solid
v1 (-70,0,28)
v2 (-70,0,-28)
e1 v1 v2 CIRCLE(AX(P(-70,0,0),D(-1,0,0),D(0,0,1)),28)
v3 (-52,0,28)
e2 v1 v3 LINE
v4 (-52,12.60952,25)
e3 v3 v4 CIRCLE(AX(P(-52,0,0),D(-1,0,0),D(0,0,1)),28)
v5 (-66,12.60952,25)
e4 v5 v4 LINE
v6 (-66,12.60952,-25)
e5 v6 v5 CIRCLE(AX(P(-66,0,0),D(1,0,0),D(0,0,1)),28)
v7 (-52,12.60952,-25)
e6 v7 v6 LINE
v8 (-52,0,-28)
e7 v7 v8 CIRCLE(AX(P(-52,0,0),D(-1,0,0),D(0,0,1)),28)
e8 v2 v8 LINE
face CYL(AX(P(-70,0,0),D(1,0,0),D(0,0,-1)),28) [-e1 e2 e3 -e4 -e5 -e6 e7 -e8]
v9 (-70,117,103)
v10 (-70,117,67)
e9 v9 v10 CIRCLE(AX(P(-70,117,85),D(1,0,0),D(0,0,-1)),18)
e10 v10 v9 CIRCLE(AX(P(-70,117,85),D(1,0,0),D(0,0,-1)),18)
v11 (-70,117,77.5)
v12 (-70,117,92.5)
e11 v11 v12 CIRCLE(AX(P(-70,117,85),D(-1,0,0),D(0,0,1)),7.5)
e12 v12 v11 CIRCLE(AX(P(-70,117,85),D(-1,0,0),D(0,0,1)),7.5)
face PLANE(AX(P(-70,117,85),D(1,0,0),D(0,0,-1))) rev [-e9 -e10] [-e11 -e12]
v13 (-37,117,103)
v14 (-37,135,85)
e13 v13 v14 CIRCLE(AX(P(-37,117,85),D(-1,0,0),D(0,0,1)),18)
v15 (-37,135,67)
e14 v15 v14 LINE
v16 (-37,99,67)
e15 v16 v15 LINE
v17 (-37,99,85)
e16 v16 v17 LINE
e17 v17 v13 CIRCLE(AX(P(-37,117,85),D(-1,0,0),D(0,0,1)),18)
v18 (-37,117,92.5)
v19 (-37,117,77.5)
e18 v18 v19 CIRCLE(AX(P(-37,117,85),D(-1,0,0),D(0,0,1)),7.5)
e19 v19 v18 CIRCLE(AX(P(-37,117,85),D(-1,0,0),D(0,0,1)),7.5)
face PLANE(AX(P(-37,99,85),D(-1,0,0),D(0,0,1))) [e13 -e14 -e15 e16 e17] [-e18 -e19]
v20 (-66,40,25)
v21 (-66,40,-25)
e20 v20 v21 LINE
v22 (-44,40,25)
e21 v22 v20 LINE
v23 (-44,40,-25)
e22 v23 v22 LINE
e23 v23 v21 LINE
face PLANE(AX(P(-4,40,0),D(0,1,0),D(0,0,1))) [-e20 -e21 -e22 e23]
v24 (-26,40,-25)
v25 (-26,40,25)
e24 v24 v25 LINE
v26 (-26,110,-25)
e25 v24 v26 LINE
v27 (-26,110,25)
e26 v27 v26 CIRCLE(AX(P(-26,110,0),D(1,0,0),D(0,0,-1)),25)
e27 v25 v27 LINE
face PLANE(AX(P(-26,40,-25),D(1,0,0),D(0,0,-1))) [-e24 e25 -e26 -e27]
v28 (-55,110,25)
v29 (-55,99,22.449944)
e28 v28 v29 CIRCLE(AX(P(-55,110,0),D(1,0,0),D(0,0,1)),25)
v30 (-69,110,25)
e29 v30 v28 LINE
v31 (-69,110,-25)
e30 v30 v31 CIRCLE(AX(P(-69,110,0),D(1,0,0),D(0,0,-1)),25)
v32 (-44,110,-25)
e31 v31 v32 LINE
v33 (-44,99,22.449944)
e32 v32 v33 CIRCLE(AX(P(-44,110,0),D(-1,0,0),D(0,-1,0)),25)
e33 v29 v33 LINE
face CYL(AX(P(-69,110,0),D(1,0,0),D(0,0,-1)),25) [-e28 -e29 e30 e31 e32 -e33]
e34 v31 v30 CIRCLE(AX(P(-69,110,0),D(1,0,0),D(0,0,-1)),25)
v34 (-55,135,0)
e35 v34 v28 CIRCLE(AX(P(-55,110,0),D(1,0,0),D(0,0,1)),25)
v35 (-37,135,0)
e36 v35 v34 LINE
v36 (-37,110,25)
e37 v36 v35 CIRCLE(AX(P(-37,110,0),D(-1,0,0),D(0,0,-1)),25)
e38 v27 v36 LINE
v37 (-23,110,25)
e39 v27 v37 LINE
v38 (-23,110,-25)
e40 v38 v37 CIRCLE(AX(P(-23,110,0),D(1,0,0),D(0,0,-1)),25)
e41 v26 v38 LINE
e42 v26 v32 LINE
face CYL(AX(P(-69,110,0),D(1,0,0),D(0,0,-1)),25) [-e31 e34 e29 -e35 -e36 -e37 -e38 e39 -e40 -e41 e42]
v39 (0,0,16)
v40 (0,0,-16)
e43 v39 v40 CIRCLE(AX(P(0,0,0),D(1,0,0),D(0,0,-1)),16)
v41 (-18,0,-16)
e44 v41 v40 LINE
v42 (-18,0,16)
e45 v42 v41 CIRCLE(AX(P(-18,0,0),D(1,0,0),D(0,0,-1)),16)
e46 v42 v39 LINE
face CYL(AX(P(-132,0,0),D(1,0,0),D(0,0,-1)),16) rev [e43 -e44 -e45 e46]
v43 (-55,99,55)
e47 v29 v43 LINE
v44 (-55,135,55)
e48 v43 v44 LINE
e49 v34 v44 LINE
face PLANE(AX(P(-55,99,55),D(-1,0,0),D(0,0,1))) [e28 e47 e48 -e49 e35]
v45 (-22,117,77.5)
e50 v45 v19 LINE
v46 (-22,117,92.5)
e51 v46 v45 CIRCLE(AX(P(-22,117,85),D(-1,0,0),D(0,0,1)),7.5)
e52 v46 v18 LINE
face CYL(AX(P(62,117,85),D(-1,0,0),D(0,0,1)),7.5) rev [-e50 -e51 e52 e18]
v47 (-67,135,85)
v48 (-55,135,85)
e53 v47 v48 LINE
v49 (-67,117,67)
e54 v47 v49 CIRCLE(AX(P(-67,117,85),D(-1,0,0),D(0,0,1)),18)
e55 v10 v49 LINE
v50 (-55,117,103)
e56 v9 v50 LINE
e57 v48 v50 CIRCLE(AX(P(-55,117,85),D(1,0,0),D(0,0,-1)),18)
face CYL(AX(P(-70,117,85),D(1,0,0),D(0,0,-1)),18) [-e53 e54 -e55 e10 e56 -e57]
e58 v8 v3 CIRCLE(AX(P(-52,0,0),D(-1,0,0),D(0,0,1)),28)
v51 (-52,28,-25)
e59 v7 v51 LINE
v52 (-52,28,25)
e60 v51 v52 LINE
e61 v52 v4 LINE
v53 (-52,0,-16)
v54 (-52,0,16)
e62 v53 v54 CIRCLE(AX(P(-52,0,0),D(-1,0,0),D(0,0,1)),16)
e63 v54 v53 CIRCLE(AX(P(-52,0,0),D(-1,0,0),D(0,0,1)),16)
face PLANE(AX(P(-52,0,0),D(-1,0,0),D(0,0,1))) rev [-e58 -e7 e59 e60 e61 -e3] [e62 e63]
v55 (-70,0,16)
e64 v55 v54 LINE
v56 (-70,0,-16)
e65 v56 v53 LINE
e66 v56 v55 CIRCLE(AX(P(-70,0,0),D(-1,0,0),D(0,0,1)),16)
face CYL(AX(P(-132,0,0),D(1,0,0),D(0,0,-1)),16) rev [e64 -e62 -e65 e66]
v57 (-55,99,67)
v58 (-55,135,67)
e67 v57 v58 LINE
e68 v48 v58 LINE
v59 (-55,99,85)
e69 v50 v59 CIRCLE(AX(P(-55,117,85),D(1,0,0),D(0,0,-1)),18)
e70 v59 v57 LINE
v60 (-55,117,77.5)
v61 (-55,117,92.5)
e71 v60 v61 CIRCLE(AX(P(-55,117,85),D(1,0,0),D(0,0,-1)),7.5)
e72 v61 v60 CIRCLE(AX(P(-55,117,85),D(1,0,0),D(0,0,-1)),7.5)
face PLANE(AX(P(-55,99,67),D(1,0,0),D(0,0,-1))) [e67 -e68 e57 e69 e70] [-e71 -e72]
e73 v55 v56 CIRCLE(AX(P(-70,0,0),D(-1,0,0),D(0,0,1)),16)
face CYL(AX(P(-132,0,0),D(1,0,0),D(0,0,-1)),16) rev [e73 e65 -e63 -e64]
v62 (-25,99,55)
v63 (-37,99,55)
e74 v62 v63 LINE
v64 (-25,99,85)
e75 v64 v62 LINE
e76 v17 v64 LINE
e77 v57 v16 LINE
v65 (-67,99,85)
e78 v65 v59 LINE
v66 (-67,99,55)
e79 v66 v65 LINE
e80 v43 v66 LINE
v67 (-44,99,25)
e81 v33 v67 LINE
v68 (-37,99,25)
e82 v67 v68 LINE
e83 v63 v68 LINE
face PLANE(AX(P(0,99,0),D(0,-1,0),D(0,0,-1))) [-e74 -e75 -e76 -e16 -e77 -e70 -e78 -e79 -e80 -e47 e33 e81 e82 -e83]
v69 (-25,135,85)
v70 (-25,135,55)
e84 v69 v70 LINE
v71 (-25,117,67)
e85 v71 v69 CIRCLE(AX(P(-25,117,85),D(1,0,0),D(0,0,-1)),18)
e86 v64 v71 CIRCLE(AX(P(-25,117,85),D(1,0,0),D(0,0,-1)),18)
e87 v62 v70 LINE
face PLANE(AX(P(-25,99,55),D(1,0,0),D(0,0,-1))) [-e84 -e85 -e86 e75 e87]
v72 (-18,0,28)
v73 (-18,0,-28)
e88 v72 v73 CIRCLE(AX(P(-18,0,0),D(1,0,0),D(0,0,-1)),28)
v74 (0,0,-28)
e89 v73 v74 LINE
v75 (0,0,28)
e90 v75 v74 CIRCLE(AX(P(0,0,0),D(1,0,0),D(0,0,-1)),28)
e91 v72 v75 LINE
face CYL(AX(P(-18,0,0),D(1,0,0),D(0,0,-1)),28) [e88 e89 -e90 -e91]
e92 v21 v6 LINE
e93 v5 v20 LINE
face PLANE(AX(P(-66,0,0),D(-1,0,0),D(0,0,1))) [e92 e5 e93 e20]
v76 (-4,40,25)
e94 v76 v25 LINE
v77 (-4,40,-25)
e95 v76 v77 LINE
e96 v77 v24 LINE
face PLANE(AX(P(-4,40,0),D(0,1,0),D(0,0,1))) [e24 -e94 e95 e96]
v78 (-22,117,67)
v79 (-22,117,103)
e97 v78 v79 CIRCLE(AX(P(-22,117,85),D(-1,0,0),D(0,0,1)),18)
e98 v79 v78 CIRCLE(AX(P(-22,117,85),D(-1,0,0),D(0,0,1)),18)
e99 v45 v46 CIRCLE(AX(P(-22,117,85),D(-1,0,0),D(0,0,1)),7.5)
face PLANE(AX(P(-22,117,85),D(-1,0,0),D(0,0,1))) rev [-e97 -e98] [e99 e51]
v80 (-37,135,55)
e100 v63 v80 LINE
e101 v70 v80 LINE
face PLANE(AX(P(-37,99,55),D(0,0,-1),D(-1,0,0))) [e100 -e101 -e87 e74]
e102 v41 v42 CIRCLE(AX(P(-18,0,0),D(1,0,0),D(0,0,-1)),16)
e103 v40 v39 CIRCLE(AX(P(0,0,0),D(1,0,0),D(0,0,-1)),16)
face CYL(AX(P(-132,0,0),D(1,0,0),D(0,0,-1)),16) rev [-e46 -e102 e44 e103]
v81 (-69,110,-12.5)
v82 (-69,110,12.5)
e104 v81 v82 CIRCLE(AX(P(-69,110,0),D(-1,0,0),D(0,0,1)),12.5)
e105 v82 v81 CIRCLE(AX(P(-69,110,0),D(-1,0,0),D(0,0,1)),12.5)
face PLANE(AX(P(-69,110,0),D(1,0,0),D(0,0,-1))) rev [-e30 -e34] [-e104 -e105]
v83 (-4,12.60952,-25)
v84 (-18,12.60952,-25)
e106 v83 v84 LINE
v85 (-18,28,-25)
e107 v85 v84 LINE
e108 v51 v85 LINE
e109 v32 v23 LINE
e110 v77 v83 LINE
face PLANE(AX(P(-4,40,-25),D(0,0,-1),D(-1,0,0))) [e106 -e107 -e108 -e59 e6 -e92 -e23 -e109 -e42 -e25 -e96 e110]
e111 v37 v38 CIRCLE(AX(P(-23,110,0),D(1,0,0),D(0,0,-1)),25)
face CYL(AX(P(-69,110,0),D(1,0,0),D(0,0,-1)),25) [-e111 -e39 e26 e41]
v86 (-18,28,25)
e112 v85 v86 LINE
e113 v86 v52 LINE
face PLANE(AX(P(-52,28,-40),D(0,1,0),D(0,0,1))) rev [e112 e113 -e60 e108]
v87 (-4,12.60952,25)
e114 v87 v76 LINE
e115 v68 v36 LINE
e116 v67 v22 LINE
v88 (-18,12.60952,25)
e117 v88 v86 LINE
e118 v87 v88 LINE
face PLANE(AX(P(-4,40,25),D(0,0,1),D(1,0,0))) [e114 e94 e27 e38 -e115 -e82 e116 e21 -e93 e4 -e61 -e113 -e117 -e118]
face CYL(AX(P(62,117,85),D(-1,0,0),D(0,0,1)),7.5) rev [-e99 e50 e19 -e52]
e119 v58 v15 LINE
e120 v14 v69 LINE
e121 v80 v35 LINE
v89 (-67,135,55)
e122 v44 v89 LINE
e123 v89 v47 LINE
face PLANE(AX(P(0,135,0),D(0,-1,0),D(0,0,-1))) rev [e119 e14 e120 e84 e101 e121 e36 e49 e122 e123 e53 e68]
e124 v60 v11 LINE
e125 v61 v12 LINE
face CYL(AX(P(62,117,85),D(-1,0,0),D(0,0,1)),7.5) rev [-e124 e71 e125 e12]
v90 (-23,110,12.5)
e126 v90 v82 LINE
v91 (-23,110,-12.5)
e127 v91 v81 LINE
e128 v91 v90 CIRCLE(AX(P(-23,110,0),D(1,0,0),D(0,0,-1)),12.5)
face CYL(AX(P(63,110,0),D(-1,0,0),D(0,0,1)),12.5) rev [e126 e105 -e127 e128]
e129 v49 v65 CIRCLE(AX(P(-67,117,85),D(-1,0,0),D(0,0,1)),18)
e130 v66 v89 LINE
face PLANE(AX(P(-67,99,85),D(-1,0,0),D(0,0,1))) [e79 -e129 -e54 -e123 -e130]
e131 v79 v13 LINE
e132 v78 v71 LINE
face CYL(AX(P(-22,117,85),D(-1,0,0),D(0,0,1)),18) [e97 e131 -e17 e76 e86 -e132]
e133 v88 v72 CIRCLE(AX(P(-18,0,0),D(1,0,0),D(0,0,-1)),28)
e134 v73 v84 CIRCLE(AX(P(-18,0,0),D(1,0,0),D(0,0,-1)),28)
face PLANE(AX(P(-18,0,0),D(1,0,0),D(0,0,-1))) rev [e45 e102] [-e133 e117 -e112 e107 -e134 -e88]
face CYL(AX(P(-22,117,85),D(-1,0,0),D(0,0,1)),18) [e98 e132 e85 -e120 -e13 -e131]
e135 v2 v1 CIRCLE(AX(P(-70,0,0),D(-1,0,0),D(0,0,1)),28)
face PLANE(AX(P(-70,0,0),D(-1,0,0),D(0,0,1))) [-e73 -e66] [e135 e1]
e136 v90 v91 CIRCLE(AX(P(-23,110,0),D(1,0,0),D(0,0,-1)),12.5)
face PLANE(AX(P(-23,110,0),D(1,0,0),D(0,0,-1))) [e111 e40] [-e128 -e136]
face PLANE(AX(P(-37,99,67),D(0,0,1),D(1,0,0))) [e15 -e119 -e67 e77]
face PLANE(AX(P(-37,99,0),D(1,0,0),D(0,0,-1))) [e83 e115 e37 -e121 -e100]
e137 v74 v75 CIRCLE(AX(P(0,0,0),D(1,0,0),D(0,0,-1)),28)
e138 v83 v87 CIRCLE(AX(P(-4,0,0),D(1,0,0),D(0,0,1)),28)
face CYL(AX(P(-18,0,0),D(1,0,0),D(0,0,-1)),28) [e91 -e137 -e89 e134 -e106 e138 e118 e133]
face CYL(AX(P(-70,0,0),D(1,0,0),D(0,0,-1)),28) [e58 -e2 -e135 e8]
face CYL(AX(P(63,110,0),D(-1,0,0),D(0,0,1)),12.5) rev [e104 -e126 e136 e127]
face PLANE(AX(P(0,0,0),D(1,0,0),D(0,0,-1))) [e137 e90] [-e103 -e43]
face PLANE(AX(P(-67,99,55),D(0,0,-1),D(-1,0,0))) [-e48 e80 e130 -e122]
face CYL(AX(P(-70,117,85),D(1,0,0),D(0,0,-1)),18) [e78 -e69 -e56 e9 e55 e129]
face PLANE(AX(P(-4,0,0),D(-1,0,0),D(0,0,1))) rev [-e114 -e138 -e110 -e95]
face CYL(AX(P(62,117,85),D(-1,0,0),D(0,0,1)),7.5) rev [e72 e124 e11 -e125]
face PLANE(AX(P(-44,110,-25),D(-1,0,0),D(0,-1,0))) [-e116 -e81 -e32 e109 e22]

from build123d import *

# Parameters (mm, degrees)
LOWER_HUB_A_SKETCH_R        = 28
LOWER_HUB_A_56_DEPTH        = 18
LOWER_HUB_B_SKETCH_R        = 28
LOWER_HUB_B_56_DEPTH        = 18
LOWER_FORK_BLOCK_DEPTH      = 48
LOWER_FORK_BLOCK_DEPTH_BACK = 14
LOWER_FORK_SLOT_SKETCH_W    = 34
LOWER_FORK_SLOT_SKETCH_H    = 15.390479787
LOWER_FORK_SLOT_DEPTH       = 65
VERTICAL_ARM_DEPTH          = 50
UPPER_HUB_DEPTH             = 3
UPPER_HUB_DEPTH_BACK        = 43
UPPER_HUB_SKETCH_R          = 25
UPPER_FORK_ARM_DEPTH        = 36
FORK_EYE_A_SKETCH_R         = 18
FORK_EYE_A_36_DEPTH         = 15
FORK_START                  = -15
FORK_EYE_B_SKETCH_R         = 18
FORK_EYE_B_DEPTH            = 15
LOWER_PIVOT_BORE_SKETCH_R   = 16
LOWER_PIVOT_BORE_32_DEPTH   = 132
UPPER_HUB_BORE_SKETCH_R     = 12.5
UPPER_HUB_BORE_25_DEPTH     = 132
FORK_EYE_BORE_SKETCH_R      = 7.5
FORK_EYE_BORE_15_DEPTH      = 132


with BuildPart() as part:
    # Lower Hub A Sketch → Lower Hub A Ø56 (new body)
    with BuildSketch(Plane(origin=(0, 0, 0), x_dir=(0, 0, -1), z_dir=(1, 0, 0))):
        Circle(LOWER_HUB_A_SKETCH_R)
    extrude(amount=-LOWER_HUB_A_56_DEPTH)



with BuildPart() as body_2:
    # Lower Hub B Sketch → Lower Hub B Ø56 (new body)
    with BuildSketch(Plane.ZY.offset(52)):
        with Locations(Location((0, 0, 0), (0, 0, 180))):
            Circle(LOWER_HUB_B_SKETCH_R)
    extrude(amount=LOWER_HUB_B_56_DEPTH)


with BuildPart() as part_1:
    add(part.part)

    add(body_2.part)  # Lower Fork Block merges body 2
    # Lower Fork Block Sketch → Lower Fork Block (add, two sides: drawn at the far end of the back side and taken through both)
    with BuildSketch(Plane.ZY.offset(18).offset(-LOWER_FORK_BLOCK_DEPTH_BACK)):
        with BuildLine():
            Line((0, 40), (25, 40))
            Line((25, 40), (25, 12.609520213))
            ThreePointArc((25, 12.609520213), (0, 28), (-25, 12.609520213))
            Line((-25, 12.609520213), (-25, 40))
            Line((-25, 40), (0, 40))
        make_face()
    extrude(amount=LOWER_FORK_BLOCK_DEPTH + LOWER_FORK_BLOCK_DEPTH_BACK)

    # Lower Fork Slot Sketch → Lower Fork Slot (cut)
    with BuildSketch(Plane.XY.offset(25)):
        with Locations((-35, 20.304760107)):
            Rectangle(LOWER_FORK_SLOT_SKETCH_W, LOWER_FORK_SLOT_SKETCH_H)
    extrude(amount=-LOWER_FORK_SLOT_DEPTH, mode=Mode.SUBTRACT)

    # Vertical Arm Sketch → Vertical Arm (add)
    with BuildSketch(Plane.XY.offset(25)):
        Polygon((-35, 40), (-26, 40), (-26, 110), (-44, 110), (-44, 40), align=None)
    extrude(amount=-VERTICAL_ARM_DEPTH)

    # Upper Hub Sketch → Upper Hub (add, two sides: drawn at the far end of the back side and taken through both)
    with BuildSketch(Plane(origin=(-26, 0, 0), x_dir=(0, 0, -1), z_dir=(1, 0, 0)).offset(-UPPER_HUB_DEPTH_BACK)):
        with Locations((0, 110)):
            Circle(UPPER_HUB_SKETCH_R)
    extrude(amount=UPPER_HUB_DEPTH + UPPER_HUB_DEPTH_BACK)

    # Upper Fork Arm Sketch → Upper Fork Arm (add)
    with BuildSketch(Plane(origin=(0, 135, 0), x_dir=(1, 0, 0), z_dir=(0, 1, 0))):
        Polygon((-37, 0), (-37, -55), (-25, -55), (-25, -85), (-37, -85), (-37, -67), (-55, -67), (-55, -85), (-67, -85), (-67, -55), (-55, -55), (-55, 0), align=None)
    extrude(amount=-UPPER_FORK_ARM_DEPTH)

    # Fork Eye A Sketch → Fork Eye A Ø36 (add)
    with BuildSketch(Plane(origin=(-55, 0, 0), x_dir=(0, 0, -1), z_dir=(1, 0, 0))):
        with Locations((-85, 117)):
            Circle(FORK_EYE_A_SKETCH_R)
    extrude(amount=-FORK_EYE_A_36_DEPTH)

    # Fork Eye B Sketch → Fork Eye B (add)
    with BuildSketch(Plane.ZY.offset(37).offset(FORK_START)):
        with Locations(Location((85, 117, 0), (0, 0, 180))):
            Circle(FORK_EYE_B_SKETCH_R)
    extrude(amount=FORK_EYE_B_DEPTH)

    # Lower Pivot Bore Sketch → Lower Pivot Bore Ø32 (cut)
    with BuildSketch(Plane(origin=(0, 0, 0), x_dir=(0, 0, -1), z_dir=(1, 0, 0))):
        with Locations(Location((0, 0, 0), (0, 0, 180))):
            Circle(LOWER_PIVOT_BORE_SKETCH_R)
    extrude(amount=-LOWER_PIVOT_BORE_32_DEPTH, mode=Mode.SUBTRACT)

    # Upper Hub Bore Sketch → Upper Hub Bore Ø25 (cut)
    with BuildSketch(Plane.ZY.offset(69)):
        with Locations((0, 110)):
            Circle(UPPER_HUB_BORE_SKETCH_R)
    extrude(amount=-UPPER_HUB_BORE_25_DEPTH, mode=Mode.SUBTRACT)

    # Fork Eye Bore Sketch → Fork Eye Bore Ø15 (cut)
    with BuildSketch(Plane.ZY.offset(70)):
        with Locations((85, 117)):
            Circle(FORK_EYE_BORE_SKETCH_R)
    extrude(amount=-FORK_EYE_BORE_15_DEPTH, mode=Mode.SUBTRACT)


solid = part_1.part
